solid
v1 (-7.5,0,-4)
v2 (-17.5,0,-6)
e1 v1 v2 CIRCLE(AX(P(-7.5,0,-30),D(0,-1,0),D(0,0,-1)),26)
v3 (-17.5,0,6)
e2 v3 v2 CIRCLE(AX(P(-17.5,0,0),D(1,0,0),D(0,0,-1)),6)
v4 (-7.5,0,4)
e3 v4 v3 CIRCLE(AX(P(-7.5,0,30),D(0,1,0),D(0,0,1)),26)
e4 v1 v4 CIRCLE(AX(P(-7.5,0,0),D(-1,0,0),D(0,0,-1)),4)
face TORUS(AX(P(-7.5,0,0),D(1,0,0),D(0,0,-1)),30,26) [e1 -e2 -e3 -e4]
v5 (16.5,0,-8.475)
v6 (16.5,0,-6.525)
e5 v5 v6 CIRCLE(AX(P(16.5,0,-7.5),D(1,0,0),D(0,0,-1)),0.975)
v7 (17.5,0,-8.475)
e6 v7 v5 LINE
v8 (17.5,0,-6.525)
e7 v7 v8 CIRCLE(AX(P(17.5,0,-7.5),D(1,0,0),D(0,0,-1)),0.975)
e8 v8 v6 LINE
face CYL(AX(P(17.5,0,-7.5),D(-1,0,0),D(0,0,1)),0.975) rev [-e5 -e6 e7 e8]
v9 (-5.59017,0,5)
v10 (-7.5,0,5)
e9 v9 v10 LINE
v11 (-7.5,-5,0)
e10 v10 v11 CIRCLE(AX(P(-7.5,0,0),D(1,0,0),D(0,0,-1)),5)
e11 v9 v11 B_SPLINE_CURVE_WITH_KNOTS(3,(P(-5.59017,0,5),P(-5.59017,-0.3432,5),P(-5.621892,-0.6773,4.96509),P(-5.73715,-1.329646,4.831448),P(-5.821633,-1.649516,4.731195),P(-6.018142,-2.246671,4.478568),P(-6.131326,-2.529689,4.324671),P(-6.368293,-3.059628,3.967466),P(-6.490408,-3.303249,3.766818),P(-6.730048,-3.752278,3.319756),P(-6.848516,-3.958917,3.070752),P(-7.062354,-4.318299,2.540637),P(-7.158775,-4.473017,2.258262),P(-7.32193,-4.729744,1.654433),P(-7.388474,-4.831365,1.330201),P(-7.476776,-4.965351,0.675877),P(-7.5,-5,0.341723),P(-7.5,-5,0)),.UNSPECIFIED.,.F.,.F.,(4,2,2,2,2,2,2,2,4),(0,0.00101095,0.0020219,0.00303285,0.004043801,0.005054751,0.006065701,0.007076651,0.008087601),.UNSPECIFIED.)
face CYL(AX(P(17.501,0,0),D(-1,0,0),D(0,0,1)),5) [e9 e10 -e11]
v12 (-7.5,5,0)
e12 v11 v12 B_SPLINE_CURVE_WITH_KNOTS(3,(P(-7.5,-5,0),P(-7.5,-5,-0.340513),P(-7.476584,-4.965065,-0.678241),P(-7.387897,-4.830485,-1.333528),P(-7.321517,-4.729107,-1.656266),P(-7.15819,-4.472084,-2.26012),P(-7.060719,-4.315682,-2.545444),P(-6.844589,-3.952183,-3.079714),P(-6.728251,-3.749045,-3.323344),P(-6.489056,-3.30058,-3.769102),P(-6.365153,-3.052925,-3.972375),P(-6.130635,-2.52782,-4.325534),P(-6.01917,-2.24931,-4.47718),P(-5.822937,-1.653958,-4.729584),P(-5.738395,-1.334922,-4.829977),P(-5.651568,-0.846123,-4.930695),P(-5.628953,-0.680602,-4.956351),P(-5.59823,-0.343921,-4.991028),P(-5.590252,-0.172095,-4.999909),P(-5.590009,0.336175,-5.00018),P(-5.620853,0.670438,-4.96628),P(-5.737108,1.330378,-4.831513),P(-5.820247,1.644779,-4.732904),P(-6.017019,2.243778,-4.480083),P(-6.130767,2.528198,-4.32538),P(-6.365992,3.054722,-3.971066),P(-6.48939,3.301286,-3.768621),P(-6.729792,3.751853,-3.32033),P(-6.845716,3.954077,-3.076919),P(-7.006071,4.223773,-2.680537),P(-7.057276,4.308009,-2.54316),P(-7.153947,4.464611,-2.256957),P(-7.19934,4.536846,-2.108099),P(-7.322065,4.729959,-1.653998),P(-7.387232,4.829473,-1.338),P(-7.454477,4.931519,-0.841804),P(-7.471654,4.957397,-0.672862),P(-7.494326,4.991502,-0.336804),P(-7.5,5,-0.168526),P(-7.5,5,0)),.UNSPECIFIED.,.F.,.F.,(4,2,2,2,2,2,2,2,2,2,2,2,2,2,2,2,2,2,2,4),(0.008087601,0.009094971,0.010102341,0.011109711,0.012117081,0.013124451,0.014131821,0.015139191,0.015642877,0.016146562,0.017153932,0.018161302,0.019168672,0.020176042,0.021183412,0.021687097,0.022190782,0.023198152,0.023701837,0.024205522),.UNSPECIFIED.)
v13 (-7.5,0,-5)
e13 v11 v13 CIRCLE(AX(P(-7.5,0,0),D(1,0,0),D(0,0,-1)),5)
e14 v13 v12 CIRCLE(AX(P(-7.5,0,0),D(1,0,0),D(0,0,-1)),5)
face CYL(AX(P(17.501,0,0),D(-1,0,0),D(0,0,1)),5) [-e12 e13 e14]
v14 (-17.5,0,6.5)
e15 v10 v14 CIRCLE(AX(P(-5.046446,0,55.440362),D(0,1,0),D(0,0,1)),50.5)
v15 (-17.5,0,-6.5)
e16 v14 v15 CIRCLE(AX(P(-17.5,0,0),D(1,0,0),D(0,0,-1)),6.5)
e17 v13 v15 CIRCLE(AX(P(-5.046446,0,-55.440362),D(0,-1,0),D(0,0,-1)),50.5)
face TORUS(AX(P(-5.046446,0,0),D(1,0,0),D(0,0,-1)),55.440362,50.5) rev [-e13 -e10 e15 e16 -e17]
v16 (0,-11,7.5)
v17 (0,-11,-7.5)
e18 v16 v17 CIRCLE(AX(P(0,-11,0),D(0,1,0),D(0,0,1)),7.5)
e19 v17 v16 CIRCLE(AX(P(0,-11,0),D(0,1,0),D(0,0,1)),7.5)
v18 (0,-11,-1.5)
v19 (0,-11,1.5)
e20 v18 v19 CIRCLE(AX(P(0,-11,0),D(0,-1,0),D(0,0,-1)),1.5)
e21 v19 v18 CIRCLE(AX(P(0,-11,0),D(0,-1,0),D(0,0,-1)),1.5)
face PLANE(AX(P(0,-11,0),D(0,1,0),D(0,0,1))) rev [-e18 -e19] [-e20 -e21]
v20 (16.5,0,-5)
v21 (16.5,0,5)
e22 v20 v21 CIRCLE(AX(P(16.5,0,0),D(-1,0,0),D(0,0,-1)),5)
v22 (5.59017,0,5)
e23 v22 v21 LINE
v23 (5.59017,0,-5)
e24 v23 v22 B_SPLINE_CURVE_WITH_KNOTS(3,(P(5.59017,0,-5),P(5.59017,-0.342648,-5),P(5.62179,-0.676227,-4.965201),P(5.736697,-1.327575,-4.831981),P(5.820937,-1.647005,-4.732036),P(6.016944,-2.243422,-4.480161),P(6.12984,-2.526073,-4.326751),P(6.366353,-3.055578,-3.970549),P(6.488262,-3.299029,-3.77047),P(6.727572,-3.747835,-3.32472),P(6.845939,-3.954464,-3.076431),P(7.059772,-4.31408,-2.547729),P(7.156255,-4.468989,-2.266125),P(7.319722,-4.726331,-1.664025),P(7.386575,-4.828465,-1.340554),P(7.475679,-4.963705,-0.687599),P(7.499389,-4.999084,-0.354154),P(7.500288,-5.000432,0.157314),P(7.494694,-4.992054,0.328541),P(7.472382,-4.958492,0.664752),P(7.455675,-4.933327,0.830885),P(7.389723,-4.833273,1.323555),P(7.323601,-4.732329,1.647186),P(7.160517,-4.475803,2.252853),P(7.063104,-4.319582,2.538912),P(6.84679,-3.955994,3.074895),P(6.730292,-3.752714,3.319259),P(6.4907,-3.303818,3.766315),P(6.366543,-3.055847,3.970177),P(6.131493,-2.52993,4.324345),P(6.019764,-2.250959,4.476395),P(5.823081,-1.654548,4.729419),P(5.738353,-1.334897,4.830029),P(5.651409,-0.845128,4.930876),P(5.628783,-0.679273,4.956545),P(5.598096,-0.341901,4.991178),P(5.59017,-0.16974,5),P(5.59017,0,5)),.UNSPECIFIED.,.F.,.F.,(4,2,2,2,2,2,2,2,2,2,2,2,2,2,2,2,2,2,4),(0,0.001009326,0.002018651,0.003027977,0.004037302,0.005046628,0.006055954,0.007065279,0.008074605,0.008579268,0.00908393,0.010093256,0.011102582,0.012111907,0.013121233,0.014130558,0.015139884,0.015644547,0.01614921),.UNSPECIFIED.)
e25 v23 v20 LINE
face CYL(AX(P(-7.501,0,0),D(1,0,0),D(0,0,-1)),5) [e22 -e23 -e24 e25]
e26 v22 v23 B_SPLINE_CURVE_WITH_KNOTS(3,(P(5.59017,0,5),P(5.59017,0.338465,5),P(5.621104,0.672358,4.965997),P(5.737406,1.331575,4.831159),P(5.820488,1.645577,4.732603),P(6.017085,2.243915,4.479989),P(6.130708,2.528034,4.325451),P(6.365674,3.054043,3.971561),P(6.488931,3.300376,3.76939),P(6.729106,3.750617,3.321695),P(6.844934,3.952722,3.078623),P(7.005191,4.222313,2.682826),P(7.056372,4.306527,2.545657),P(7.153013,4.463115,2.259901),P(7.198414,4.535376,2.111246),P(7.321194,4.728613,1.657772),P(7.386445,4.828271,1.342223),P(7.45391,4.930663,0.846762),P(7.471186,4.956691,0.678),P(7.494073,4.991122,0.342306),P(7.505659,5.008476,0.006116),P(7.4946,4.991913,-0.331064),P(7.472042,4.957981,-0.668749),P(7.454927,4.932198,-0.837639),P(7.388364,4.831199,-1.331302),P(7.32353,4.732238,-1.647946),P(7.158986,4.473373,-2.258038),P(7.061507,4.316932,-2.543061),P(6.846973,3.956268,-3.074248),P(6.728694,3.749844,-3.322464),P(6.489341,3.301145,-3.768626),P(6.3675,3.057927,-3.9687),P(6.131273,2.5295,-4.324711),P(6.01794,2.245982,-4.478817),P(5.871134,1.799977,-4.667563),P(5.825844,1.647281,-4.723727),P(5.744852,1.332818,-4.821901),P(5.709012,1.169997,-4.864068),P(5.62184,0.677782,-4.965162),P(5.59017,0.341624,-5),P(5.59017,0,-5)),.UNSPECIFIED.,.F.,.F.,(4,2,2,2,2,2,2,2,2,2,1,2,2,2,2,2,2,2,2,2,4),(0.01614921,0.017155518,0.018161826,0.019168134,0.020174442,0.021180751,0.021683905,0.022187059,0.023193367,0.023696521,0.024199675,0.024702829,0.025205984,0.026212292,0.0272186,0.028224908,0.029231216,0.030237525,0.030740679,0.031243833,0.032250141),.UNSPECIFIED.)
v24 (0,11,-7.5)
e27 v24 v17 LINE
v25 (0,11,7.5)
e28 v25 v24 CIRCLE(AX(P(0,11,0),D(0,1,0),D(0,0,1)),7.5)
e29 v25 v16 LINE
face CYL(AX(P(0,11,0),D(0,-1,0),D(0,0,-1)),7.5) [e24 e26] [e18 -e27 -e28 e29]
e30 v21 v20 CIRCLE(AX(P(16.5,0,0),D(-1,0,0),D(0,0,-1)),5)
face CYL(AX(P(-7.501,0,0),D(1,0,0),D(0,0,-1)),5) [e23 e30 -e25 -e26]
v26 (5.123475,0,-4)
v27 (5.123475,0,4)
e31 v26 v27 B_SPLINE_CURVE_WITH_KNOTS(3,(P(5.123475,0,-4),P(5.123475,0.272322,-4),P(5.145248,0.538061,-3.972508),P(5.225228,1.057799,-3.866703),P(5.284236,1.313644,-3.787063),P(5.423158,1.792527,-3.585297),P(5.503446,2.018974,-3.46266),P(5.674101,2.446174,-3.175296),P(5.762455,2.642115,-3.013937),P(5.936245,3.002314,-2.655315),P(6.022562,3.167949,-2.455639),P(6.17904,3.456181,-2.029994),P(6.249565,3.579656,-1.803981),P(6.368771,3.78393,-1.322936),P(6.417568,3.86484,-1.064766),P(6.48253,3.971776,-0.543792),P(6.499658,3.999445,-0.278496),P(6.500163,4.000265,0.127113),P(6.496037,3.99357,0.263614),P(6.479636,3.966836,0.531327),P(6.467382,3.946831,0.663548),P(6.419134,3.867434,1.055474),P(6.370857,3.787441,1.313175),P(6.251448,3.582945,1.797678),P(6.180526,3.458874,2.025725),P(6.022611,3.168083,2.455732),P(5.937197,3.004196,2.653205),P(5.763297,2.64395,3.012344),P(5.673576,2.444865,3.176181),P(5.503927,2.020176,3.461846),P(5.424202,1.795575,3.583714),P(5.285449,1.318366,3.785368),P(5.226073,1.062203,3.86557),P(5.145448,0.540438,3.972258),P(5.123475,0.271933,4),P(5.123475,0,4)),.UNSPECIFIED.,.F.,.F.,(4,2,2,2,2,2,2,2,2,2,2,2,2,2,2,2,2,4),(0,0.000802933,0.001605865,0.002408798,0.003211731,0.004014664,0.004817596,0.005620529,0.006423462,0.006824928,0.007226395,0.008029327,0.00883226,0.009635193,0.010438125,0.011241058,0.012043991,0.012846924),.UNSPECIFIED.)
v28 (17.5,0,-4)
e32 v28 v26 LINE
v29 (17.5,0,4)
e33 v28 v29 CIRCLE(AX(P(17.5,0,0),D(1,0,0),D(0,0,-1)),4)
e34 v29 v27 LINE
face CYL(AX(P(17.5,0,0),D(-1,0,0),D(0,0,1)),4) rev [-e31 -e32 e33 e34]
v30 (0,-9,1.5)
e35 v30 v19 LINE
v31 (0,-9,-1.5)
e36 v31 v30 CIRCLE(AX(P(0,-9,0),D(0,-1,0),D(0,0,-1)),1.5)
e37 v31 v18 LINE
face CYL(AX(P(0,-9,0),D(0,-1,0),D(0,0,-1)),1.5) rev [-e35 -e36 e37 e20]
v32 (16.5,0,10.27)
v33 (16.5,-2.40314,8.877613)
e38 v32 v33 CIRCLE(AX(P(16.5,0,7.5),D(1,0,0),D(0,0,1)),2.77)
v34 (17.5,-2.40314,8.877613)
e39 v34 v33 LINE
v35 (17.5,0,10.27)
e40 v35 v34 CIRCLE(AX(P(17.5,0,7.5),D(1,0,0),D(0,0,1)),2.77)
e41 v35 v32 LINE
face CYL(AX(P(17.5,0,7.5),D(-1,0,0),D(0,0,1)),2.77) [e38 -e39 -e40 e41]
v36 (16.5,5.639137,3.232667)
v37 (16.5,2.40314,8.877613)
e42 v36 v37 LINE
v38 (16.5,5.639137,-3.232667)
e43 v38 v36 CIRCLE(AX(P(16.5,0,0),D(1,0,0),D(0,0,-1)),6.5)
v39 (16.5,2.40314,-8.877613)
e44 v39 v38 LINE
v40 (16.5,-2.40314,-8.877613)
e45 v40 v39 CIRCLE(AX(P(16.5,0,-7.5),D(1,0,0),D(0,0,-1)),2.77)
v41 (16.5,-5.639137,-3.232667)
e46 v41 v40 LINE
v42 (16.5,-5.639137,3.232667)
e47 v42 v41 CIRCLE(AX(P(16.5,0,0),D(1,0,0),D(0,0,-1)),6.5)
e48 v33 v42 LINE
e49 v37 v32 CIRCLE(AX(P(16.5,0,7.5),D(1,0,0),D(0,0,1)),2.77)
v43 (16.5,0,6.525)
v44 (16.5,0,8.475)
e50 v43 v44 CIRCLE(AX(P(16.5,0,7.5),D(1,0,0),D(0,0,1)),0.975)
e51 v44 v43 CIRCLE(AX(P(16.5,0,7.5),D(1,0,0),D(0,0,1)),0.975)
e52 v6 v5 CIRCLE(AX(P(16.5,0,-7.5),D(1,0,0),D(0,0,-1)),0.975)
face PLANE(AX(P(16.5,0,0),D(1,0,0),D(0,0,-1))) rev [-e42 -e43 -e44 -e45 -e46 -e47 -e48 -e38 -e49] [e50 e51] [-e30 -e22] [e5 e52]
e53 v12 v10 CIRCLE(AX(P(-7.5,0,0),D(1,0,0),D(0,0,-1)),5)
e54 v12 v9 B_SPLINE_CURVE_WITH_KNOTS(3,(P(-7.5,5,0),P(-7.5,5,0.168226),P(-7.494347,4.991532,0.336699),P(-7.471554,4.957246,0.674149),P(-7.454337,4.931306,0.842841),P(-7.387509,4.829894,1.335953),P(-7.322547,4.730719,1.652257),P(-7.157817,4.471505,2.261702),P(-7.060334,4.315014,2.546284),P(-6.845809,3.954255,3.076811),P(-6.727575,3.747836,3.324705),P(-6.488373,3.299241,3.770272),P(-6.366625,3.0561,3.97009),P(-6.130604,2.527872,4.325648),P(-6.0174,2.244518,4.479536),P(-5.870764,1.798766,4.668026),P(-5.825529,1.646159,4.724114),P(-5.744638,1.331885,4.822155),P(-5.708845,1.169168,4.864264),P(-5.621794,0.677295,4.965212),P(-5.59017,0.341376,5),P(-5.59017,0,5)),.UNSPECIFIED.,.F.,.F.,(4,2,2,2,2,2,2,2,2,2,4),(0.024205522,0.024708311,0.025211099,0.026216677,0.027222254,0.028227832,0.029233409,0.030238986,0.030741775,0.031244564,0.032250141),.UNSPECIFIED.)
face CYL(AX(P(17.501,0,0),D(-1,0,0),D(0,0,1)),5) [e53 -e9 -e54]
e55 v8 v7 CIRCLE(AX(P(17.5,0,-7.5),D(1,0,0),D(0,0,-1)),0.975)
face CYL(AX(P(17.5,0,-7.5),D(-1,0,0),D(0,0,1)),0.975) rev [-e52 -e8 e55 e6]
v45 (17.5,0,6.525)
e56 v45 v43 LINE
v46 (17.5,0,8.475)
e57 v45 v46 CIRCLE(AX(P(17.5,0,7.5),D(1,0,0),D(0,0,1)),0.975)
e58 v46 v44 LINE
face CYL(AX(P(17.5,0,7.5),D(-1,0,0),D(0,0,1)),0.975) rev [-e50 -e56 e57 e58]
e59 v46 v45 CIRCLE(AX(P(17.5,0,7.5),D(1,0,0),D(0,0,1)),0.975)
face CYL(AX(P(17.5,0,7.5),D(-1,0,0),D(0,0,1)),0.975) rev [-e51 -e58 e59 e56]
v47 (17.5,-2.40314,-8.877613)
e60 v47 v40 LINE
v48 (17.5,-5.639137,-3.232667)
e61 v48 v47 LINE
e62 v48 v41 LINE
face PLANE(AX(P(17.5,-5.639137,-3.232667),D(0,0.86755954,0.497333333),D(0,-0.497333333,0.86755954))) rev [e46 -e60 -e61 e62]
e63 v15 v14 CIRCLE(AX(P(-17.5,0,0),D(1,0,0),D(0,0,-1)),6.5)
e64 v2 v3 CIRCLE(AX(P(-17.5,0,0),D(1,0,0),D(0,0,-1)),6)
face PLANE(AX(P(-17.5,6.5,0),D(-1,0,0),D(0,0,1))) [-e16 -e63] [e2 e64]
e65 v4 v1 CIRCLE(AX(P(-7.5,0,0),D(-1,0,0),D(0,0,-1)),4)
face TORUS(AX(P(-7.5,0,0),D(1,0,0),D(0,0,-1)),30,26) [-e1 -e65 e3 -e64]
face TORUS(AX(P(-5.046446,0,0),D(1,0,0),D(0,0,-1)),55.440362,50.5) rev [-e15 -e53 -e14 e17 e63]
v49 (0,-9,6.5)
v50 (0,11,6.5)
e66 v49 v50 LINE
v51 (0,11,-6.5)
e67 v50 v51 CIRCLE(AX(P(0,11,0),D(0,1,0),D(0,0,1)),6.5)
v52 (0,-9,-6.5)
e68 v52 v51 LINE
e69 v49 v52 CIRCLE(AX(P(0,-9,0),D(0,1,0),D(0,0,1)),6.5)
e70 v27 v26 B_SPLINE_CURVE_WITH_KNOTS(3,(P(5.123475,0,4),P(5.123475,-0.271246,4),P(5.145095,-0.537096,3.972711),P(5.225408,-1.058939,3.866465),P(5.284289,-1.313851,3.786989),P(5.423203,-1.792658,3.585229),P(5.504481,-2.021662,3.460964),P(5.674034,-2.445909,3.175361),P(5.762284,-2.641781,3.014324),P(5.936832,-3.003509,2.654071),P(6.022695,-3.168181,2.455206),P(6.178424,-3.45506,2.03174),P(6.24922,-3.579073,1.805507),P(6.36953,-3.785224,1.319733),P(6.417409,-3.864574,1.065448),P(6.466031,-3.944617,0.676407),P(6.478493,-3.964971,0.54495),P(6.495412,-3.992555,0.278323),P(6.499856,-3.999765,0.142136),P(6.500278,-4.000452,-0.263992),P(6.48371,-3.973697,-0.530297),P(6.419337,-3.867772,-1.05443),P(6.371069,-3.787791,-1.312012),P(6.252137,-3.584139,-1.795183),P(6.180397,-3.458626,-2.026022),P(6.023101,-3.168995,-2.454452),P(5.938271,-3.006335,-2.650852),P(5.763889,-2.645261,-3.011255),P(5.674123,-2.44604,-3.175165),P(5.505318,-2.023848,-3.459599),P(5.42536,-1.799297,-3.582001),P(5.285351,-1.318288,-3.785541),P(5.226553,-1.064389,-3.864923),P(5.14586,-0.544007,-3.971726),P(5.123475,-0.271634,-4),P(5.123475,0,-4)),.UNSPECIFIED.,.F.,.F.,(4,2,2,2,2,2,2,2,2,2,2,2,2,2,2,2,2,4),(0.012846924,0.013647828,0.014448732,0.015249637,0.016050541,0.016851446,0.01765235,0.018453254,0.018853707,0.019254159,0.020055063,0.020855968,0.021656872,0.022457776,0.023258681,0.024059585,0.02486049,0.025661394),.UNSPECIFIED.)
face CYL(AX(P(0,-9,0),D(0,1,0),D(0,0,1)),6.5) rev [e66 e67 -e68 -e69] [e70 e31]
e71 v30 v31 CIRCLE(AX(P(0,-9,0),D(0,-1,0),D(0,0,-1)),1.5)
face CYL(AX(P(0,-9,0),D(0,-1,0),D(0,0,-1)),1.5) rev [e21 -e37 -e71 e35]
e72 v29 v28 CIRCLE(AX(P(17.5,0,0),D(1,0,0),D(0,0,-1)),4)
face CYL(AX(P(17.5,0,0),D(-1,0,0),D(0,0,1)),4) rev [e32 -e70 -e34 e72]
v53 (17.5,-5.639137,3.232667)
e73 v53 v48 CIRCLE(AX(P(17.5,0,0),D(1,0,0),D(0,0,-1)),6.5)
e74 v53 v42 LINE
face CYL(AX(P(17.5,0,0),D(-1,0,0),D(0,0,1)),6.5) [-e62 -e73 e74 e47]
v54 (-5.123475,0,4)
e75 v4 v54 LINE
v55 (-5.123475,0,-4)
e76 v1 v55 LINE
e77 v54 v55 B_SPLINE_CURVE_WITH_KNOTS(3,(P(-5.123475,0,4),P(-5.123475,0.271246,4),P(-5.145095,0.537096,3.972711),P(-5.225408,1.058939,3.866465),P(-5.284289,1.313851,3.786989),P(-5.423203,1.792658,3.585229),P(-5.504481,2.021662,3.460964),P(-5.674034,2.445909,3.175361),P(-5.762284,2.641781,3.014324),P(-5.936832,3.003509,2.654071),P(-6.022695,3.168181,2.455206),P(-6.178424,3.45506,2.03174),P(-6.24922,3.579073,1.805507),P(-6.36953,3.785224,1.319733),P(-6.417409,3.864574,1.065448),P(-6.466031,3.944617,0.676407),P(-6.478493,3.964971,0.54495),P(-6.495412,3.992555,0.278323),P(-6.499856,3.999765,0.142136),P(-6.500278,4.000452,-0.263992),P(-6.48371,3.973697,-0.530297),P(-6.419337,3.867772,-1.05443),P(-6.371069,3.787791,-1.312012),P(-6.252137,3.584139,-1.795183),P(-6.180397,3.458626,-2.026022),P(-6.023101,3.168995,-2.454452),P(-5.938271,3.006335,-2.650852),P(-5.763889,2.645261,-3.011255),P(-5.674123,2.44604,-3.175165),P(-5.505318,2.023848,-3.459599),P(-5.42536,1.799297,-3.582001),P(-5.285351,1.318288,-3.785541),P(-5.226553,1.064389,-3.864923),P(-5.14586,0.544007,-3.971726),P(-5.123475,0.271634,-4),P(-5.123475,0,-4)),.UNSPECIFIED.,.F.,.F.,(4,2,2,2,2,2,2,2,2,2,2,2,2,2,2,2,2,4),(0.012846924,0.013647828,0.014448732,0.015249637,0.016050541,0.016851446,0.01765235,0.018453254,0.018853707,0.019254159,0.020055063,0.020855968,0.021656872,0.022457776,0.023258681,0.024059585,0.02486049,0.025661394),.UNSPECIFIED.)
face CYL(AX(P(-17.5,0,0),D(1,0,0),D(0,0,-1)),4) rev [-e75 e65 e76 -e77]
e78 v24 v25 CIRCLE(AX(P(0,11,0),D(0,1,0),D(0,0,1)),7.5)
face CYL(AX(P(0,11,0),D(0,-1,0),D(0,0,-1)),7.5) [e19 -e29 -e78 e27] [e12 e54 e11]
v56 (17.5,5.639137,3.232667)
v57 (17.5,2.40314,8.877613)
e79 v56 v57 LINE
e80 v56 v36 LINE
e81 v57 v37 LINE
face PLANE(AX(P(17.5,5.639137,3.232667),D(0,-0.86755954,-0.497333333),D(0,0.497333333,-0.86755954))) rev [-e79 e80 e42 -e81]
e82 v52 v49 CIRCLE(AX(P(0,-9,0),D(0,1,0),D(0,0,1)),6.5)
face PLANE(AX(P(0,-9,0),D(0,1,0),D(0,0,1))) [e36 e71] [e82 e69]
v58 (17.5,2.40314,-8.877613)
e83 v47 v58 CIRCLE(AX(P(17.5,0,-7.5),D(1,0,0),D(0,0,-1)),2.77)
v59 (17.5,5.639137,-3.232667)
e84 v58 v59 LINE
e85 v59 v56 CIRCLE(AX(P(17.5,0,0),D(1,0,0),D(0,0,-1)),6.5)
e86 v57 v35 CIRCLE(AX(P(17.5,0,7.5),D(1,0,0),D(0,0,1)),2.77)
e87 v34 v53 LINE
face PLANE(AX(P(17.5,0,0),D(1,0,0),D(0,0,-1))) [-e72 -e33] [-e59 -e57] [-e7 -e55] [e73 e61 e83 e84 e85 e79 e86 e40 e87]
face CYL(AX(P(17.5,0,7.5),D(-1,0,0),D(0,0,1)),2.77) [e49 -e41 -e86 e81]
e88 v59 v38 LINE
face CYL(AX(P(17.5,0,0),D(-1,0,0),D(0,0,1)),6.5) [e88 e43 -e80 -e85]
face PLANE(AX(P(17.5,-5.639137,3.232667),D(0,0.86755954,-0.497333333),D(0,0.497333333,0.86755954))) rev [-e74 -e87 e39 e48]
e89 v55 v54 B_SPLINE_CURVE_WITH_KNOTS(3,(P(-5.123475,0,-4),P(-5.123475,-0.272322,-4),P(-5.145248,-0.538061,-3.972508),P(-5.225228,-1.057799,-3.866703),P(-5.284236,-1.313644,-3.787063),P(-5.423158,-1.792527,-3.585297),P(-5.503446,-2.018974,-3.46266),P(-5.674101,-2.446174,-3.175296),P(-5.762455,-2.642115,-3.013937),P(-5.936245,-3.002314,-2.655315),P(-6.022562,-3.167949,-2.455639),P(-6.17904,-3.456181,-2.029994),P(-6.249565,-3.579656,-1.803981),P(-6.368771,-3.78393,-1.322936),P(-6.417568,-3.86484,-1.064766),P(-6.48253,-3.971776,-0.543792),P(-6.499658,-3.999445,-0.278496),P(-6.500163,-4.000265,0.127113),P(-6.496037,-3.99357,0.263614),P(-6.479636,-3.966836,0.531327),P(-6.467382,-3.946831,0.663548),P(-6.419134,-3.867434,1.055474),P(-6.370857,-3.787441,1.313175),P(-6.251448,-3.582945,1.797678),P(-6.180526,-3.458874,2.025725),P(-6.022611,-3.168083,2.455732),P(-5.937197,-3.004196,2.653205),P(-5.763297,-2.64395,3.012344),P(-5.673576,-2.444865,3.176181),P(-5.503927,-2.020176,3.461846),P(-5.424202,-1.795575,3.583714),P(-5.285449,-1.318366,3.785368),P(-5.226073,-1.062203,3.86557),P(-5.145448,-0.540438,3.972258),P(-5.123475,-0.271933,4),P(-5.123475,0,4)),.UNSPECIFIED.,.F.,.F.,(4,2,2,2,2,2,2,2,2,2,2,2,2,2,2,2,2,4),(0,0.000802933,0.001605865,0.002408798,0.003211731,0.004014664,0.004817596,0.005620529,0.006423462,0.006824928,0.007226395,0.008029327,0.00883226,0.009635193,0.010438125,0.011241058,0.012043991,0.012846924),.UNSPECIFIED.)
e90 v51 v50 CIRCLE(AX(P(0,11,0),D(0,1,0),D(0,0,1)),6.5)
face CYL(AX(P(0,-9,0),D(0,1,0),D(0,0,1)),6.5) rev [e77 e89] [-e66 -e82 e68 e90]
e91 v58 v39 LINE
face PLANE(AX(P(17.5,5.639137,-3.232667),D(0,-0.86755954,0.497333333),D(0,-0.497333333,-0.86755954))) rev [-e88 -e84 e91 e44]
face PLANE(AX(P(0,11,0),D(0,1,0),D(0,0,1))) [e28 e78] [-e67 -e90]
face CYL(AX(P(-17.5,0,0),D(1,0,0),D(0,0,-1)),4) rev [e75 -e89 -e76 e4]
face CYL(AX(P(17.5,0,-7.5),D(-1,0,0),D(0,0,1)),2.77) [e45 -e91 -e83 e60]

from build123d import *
from build123d.topology import SkipClean

# Parameters (mm, degrees)
MAIN_BARREL_SKETCH_R       = 7.5
MAIN_BARREL_DEPTH          = 11
MAIN_BORE_SKETCH_13_R      = 6.5
MAIN_BORE_13_DEPTH         = 20
OUTLET_TUBE_SKETCH_10_R    = 5
OUTLET_TUBE_10_DEPTH       = 9
MOUNTING_FLANGE_SKETCH_R   = 4
MOUNTING_FLANGE_SKETCH_R_2 = 0.975
MOUNTING_FLANGE_DEPTH      = 1
OUTLET_TUBE_JOINT_REACH    = 23.248
OUTLET_TUBE_JOINT_SKETCH_R = 5
INTAKE_TUBE_10_REACH       = 31.18
INTAKE_TUBE_SKETCH_10_R    = 5
OUTLET_BORE_SKETCH_R       = 4
OUTLET_BORE_DEPTH          = 38.181620489
SIDE_PORT_SKETCH_3_R       = 1.5
SIDE_PORT_3_DEPTH          = 2


with BuildPart() as part:
    # Main Barrel Sketch → Main Barrel (new, symmetric)
    with BuildSketch(Plane(origin=(0, 0, 0), x_dir=(1, 0, 0), z_dir=(0, 1, 0))):
        with Locations(Location((0, 0, 0), (0, 0, 270))):
            Circle(MAIN_BARREL_SKETCH_R)
    extrude(amount=MAIN_BARREL_DEPTH, both=True)

    # Main Bore Sketch Ø13 → Main Bore Ø13 (cut)
    with BuildSketch(Plane(origin=(0, 11, 0), x_dir=(1, 0, 0), z_dir=(0, 1, 0))):
        with Locations(Location((0, 0, 0), (0, 0, 270))):
            Circle(MAIN_BORE_SKETCH_13_R)
    extrude(amount=-MAIN_BORE_13_DEPTH, mode=Mode.SUBTRACT)

    # Outlet Tube Joint Sketch → Outlet Tube Joint (add, up to next)
    with BuildSketch(Plane.ZY.offset(-7.5), mode=Mode.PRIVATE) as outlet_tube_joint_sk1:
        with Locations(Location((0, 0, 0), (0, 0, 180))):
            Circle(OUTLET_TUBE_JOINT_SKETCH_R)
    outlet_tube_joint_tool1 = extrude(outlet_tube_joint_sk1.sketch, amount=OUTLET_TUBE_JOINT_REACH, mode=Mode.PRIVATE) - part.part


with BuildPart() as body_2:
    # Outlet Tube Sketch Ø10 → Outlet Tube Ø10 (new body)
    with BuildSketch(Plane.ZY.offset(-7.5)):
        Circle(OUTLET_TUBE_SKETCH_10_R)
    extrude(amount=-OUTLET_TUBE_10_DEPTH)

    # Mounting Flange Sketch → Mounting Flange (add)
    with BuildSketch(Plane(origin=(16.5, 0, 0), x_dir=(0, 0, -1), z_dir=(1, 0, 0))):
        with BuildLine():
            Line((3.232666667, 5.63913701), (8.877613333, 2.403139926))
            ThreePointArc((8.877613333, 2.403139926), (10.27, 0), (8.877613333, -2.403139926))
            Line((8.877613333, -2.403139926), (3.232666667, -5.63913701))
            ThreePointArc((3.232666667, -5.63913701), (0, -6.5), (-3.232666667, -5.63913701))
            Line((-3.232666667, -5.63913701), (-8.877613333, -2.403139926))
            ThreePointArc((-8.877613333, -2.403139926), (-10.27, 0), (-8.877613333, 2.403139926))
            Line((-8.877613333, 2.403139926), (-3.232666667, 5.63913701))
            ThreePointArc((-3.232666667, 5.63913701), (0, 6.5), (3.232666667, 5.63913701))
        make_face()
        Circle(MOUNTING_FLANGE_SKETCH_R, mode=Mode.SUBTRACT)
        with Locations((7.5, 0)):
            Circle(MOUNTING_FLANGE_SKETCH_R_2, mode=Mode.SUBTRACT)
        with Locations(Location((-7.5, 0, 0), (0, 0, 180))):
            Circle(MOUNTING_FLANGE_SKETCH_R_2, mode=Mode.SUBTRACT)
    extrude(amount=MOUNTING_FLANGE_DEPTH)


with BuildPart() as part_1:
    add(part.part)

    add(body_2.part)  # Outlet Tube Joint merges body 2
    add(outlet_tube_joint_tool1.solids().sort_by_distance((7.5, 0, 0))[0])
    add(outlet_tube_joint_tool1.solids().sort_by_distance((7.5, 0, 0))[1])

    # Intake Tube Sketch Ø10 → Intake Tube Ø10 (add, up to next)
    with BuildSketch(Plane(origin=(-7.5, 0, 0), x_dir=(0, 0, -1), z_dir=(1, 0, 0)), mode=Mode.PRIVATE) as intake_tube_10_sk1:
        Circle(INTAKE_TUBE_SKETCH_10_R)
    intake_tube_10_tool1 = extrude(intake_tube_10_sk1.sketch, amount=INTAKE_TUBE_10_REACH, mode=Mode.PRIVATE) - part_1.part


with BuildPart() as body_2_2:
    # Intake Bell Profile → Intake Bell (revolve)
    with BuildSketch(Plane.XY, mode=Mode.PRIVATE) as intake_bell_sk:
        with BuildLine():
            Line((-17.5, 6.5), (-17.5, 6))
            ThreePointArc((-17.5, 6), (-12.599019514, 4.504902432), (-7.5, 4))
            Line((-7.5, 4), (-7.5, 5))
            ThreePointArc((-7.5, 5), (-12.537638643, 5.499075714), (-17.5, 6.5))
        make_face()
    revolve(intake_bell_sk.sketch.rotate(Axis((0, 0, 0), (-1, 0, 0)), 90), axis=Axis((0, 0, 0), (-1, 0, 0)))


with BuildPart() as part_2:
    add(part_1.part)

    add(body_2_2.part)  # Intake Tube Ø10 merges body 2 2
    add(intake_tube_10_tool1.solids().sort_by_distance((-7.5, 0, 0))[0])
    add(intake_tube_10_tool1.solids().sort_by_distance((-7.5, 0, 0))[1])

    # Outlet Bore Sketch → Outlet Bore (cut, through all)
    with SkipClean():  # the faces are left unmerged after this step: merging them gives an invalid solid
        with BuildSketch(Plane(origin=(16.5, 0, 0), x_dir=(0, 0, -1), z_dir=(1, 0, 0))):
            Circle(OUTLET_BORE_SKETCH_R)
        extrude(amount=-OUTLET_BORE_DEPTH, mode=Mode.SUBTRACT)

    # Side Port Sketch Ø3 → Side Port Ø3 (cut)
    with SkipClean():  # the faces are left unmerged after this step: merging them gives an invalid solid
        with BuildSketch(Plane.XZ.offset(11)):
            with Locations(Location((0, 0, 0), (0, 0, 270))):
                Circle(SIDE_PORT_SKETCH_3_R)
        extrude(amount=-SIDE_PORT_3_DEPTH, mode=Mode.SUBTRACT)


solid = part_2.part
